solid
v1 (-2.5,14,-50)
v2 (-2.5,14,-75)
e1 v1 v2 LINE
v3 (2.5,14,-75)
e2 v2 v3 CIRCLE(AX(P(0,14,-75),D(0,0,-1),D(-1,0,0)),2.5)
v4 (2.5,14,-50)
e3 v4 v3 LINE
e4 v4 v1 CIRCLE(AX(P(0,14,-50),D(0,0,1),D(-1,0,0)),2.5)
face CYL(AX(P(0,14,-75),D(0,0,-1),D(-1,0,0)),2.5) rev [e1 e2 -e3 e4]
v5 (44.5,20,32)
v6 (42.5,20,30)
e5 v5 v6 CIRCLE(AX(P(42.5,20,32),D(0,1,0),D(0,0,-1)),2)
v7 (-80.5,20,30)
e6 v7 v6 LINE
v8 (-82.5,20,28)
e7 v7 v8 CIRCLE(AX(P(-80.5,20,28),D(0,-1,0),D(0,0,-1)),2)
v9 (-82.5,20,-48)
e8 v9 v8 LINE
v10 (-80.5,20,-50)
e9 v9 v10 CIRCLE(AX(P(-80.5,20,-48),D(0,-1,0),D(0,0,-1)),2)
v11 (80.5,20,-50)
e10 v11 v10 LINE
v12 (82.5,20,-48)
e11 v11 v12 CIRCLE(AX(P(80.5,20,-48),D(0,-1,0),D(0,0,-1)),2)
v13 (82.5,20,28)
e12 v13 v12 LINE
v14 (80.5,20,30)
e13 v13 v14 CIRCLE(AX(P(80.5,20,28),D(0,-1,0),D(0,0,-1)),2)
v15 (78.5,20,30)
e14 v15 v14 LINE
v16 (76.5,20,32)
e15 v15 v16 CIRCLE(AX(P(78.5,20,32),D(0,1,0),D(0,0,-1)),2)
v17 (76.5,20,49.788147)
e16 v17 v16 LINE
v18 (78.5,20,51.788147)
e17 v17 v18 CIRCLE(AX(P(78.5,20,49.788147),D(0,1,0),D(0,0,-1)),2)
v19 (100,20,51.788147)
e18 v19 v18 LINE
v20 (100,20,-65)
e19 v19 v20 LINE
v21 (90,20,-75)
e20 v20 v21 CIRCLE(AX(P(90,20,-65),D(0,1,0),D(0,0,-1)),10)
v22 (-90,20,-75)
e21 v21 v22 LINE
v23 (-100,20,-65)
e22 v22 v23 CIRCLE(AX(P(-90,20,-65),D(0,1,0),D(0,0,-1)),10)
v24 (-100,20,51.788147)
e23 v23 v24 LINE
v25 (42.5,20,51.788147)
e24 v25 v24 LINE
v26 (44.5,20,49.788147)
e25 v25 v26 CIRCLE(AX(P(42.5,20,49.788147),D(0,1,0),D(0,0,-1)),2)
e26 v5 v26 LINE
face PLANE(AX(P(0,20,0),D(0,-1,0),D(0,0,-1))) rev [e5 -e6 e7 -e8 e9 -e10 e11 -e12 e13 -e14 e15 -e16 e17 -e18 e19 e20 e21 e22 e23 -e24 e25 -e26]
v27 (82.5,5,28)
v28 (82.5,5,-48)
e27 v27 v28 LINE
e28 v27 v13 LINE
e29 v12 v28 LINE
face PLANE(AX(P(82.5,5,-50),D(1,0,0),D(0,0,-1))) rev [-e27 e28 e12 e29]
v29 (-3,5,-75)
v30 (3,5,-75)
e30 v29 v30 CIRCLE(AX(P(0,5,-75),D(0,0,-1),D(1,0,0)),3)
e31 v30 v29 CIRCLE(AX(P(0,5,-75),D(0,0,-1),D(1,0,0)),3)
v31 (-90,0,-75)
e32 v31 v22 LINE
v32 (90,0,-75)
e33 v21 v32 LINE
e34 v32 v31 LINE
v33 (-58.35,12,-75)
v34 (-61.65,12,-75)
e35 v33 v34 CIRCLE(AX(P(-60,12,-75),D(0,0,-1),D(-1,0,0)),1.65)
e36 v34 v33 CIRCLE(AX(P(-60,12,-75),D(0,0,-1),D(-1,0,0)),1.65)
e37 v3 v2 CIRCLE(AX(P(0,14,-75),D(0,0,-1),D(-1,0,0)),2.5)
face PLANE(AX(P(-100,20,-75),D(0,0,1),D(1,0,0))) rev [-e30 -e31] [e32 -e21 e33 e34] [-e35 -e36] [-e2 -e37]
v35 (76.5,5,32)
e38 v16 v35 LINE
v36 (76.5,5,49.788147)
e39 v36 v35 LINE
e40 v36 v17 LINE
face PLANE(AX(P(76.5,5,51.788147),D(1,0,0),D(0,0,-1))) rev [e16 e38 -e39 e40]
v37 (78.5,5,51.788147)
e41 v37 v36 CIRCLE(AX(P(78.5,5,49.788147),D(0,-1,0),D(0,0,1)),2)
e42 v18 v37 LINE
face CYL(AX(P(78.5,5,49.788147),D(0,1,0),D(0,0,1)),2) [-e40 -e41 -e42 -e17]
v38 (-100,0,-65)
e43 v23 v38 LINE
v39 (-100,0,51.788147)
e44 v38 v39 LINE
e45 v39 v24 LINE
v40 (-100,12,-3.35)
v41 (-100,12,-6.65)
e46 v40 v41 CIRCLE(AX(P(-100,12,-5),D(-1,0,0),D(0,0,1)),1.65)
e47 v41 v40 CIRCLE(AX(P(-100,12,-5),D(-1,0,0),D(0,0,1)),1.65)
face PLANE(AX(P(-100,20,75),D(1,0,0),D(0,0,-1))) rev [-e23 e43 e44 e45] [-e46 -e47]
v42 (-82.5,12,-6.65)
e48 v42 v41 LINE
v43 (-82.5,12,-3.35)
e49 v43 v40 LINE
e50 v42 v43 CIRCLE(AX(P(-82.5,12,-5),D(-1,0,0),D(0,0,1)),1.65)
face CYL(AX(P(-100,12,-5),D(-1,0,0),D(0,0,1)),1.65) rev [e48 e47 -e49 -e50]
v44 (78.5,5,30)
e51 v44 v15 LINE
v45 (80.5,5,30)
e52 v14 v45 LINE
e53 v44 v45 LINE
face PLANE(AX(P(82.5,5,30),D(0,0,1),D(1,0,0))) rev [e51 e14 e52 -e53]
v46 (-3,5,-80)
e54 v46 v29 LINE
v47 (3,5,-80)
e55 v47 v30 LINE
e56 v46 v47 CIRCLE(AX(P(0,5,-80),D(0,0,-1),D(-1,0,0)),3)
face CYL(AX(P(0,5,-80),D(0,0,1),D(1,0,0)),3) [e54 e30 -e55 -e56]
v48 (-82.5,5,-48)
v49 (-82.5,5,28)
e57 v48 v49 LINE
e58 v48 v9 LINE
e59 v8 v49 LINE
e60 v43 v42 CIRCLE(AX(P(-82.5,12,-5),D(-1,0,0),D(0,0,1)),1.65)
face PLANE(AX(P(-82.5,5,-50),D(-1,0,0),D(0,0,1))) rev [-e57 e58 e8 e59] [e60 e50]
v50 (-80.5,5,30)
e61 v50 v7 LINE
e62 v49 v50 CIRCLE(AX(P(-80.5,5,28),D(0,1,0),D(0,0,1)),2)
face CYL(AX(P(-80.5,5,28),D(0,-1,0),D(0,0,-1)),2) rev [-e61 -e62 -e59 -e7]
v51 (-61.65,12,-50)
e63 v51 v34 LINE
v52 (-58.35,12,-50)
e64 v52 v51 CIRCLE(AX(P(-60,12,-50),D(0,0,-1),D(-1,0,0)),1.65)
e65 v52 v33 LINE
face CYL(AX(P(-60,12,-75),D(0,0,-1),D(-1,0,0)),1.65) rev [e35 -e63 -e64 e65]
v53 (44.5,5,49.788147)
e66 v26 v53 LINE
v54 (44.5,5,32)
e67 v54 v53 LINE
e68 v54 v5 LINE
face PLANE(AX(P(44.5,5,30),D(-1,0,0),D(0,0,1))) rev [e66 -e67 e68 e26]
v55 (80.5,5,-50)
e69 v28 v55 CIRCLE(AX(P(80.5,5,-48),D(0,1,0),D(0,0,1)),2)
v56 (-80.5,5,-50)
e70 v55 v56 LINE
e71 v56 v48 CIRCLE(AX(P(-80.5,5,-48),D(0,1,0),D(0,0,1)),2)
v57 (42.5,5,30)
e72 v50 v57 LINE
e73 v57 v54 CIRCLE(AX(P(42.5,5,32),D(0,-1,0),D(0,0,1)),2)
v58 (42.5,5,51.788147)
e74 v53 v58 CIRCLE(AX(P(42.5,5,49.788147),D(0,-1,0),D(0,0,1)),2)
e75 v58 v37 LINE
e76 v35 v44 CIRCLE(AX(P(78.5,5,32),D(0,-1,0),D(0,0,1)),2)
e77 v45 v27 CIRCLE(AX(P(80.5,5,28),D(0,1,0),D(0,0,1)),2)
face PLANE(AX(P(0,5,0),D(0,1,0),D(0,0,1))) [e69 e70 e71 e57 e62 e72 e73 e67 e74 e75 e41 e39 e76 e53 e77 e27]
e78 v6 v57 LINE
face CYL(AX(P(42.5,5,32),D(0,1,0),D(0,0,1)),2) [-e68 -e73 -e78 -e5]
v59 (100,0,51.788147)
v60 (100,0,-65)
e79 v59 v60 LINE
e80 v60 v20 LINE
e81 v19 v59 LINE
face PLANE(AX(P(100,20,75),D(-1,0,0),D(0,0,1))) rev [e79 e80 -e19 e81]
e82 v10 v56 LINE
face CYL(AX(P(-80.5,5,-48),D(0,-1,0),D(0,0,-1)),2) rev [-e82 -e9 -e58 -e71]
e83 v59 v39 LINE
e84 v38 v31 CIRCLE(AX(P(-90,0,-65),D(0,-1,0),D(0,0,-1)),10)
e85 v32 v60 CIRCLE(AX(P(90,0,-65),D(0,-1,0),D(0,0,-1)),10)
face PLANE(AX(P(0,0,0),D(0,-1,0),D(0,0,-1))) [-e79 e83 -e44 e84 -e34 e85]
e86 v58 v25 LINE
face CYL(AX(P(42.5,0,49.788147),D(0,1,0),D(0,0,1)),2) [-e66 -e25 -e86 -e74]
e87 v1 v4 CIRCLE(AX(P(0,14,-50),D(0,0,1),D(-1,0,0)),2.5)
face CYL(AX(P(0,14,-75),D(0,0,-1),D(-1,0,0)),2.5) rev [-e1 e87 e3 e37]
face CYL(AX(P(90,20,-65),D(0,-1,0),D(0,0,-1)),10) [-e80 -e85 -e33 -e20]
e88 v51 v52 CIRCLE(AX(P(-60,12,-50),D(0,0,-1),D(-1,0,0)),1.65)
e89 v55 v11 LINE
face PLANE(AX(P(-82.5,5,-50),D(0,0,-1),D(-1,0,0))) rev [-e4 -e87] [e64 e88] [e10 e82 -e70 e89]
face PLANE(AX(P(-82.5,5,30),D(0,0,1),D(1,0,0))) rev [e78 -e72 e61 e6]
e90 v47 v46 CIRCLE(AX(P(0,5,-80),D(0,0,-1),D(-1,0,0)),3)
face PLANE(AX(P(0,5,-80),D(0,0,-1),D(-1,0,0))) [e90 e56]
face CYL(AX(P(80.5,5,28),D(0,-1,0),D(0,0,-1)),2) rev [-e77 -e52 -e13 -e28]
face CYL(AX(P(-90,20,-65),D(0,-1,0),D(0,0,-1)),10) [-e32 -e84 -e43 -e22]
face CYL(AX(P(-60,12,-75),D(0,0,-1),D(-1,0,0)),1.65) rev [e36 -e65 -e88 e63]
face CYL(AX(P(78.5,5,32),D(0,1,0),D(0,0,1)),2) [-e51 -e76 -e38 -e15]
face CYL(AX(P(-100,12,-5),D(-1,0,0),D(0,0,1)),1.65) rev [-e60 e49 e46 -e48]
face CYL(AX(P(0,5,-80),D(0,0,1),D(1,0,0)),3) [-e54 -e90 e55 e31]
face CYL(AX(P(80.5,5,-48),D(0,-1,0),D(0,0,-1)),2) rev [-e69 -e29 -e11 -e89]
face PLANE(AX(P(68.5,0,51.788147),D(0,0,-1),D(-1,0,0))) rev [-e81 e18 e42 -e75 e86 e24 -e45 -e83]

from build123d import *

# Parameters (mm, degrees)
SKETCH1_W             = 200
SKETCH1_H             = 150
BOSS_EXTRUDE1_DEPTH   = 20
SKETCH2_R             = 3
BOSS_EXTRUDE2_DEPTH   = 5
M6_TAPPED_HOLE1_D     = 5
M6_TAPPED_HOLE1_DEPTH = 25
M6_TAPPED_HOLE1_TIP   = 1.502151548
CUT_EXTRUDE1_DEPTH    = 15
SKETCH6_W             = 16
SKETCH6_H             = 15
CUT_EXTRUDE2_DEPTH    = 129.937969582
FILLET1_R             = 2
M4_TAPPED_HOLE1_D     = 3.3
M4_TAPPED_HOLE1_DEPTH = 30
M4_TAPPED_HOLE1_TIP   = 0.991420021
FILLET2_R             = 10
M4_TAPPED_HOLE2_D     = 3.3
M4_TAPPED_HOLE2_DEPTH = 30
M4_TAPPED_HOLE2_TIP   = 0.991420021
CUT_EXTRUDE3_DEPTH    = 130.614813968
FILLET3_R             = 2


with BuildPart() as part:
    # Sketch1 → Boss-Extrude1 (new body)
    with BuildSketch(Plane(origin=(0, 0, 0), x_dir=(1, 0, 0), z_dir=(0, 1, 0))):
        Rectangle(SKETCH1_W, SKETCH1_H)
    extrude(amount=BOSS_EXTRUDE1_DEPTH)

    # Sketch2 → Boss-Extrude2 (add)
    with BuildSketch(Plane(origin=(0, 0, -75), x_dir=(-1, 0, 0), z_dir=(0, 0, -1))):
        with Locations(Location((0, 5, 0), (0, 0, 180))):
            Circle(SKETCH2_R)
    extrude(amount=BOSS_EXTRUDE2_DEPTH)

    # M6 Tapped Hole1
    with Locations(Plane(origin=(0, 0, -75), x_dir=(-1, 0, 0), z_dir=(0, 0, -1))):
        with Locations((0, 14)):
            Hole(M6_TAPPED_HOLE1_D / 2, depth=M6_TAPPED_HOLE1_DEPTH)
            with Locations((0, 0, -(M6_TAPPED_HOLE1_DEPTH + M6_TAPPED_HOLE1_TIP / 2))):  # 118° drill point
                Cone(0, M6_TAPPED_HOLE1_D / 2, M6_TAPPED_HOLE1_TIP, mode=Mode.SUBTRACT)

    # Sketch5 → Cut-Extrude1 (cut)
    with BuildSketch(Plane(origin=(0, 20, 0), x_dir=(1, 0, 0), z_dir=(0, 1, 0))):
        Polygon((-82.5, 50), (44.5, 50), (76.5, 50), (82.5, 50), (82.5, -30), (76.5, -30), (76.5, -51.78814737), (68.5, -51.78814737), (68.5, -66.78814737), (52.5, -66.78814737), (52.5, -51.78814737), (44.5, -51.78814737), (44.5, -30), (-82.5, -30), align=None)
    extrude(amount=-CUT_EXTRUDE1_DEPTH, mode=Mode.SUBTRACT)

    # Sketch6 → Cut-Extrude2 (cut, through all)
    with BuildSketch(Plane(origin=(0, 5, 0), x_dir=(1, 0, 0), z_dir=(0, 1, 0))):
        with Locations((60.5, -59.28814737)):
            Rectangle(SKETCH6_W, SKETCH6_H)
    extrude(amount=-CUT_EXTRUDE2_DEPTH, mode=Mode.SUBTRACT)

    # Fillet1
    fillet1_edges = [part.edges().sort_by_distance(p)[0] for p in [
        (-82.5, 12.5, -50),
        (-82.5, 12.5, 30),
        (82.5, 12.5, -50),
        (82.5, 12.5, 30),
        (76.5, 12.5, 30),
        (68.5, 12.5, 51.78814737),
        (68.5, 10, 66.78814737),
        (52.5, 10, 66.78814737),
        (52.5, 12.5, 51.78814737),
        (44.5, 12.5, 30),
    ]]
    fillet(fillet1_edges, radius=FILLET1_R)

    # M4 Tapped Hole1
    with Locations(Plane.ZY.offset(100)):
        with Locations((-5, 12)):
            Hole(M4_TAPPED_HOLE1_D / 2, depth=M4_TAPPED_HOLE1_DEPTH)
            with Locations((0, 0, -(M4_TAPPED_HOLE1_DEPTH + M4_TAPPED_HOLE1_TIP / 2))):  # 118° drill point
                Cone(0, M4_TAPPED_HOLE1_D / 2, M4_TAPPED_HOLE1_TIP, mode=Mode.SUBTRACT)

    # Fillet2
    fillet2_edges = [part.edges().sort_by_distance(p)[0] for p in [
        (100, 10, 75),
        (-100, 10, 75),
        (-100, 10, -75),
        (100, 10, -75),
    ]]
    fillet(fillet2_edges, radius=FILLET2_R)

    # M4 Tapped Hole2
    with Locations(Plane(origin=(0, 0, -75), x_dir=(-1, 0, 0), z_dir=(0, 0, -1))):
        with Locations((60, 12)):
            Hole(M4_TAPPED_HOLE2_D / 2, depth=M4_TAPPED_HOLE2_DEPTH)
            with Locations((0, 0, -(M4_TAPPED_HOLE2_DEPTH + M4_TAPPED_HOLE2_TIP / 2))):  # 118° drill point
                Cone(0, M4_TAPPED_HOLE2_D / 2, M4_TAPPED_HOLE2_TIP, mode=Mode.SUBTRACT)

    # Sketch13 → Cut-Extrude3 (cut, through all)
    with BuildSketch(Plane(origin=(0, 20, 0), x_dir=(1, 0, 0), z_dir=(0, 1, 0))):
        Polygon((73.5, -51.78814737), (115.827704394, -51.78814737), (115.827704394, -85.085952347), (72.5, -85.085952347), (-109.048113532, -107.181271315), (-117.406351495, -51.78814737), align=None)
    extrude(amount=-CUT_EXTRUDE3_DEPTH, mode=Mode.SUBTRACT)

    # Fillet3
    fillet3_edges = [part.edges().sort_by_distance(p)[0] for p in [
        (76.5, 12.5, 51.78814737),
        (44.5, 12.5, 51.78814737),
    ]]
    fillet(fillet3_edges, radius=FILLET3_R)


solid = part.part
